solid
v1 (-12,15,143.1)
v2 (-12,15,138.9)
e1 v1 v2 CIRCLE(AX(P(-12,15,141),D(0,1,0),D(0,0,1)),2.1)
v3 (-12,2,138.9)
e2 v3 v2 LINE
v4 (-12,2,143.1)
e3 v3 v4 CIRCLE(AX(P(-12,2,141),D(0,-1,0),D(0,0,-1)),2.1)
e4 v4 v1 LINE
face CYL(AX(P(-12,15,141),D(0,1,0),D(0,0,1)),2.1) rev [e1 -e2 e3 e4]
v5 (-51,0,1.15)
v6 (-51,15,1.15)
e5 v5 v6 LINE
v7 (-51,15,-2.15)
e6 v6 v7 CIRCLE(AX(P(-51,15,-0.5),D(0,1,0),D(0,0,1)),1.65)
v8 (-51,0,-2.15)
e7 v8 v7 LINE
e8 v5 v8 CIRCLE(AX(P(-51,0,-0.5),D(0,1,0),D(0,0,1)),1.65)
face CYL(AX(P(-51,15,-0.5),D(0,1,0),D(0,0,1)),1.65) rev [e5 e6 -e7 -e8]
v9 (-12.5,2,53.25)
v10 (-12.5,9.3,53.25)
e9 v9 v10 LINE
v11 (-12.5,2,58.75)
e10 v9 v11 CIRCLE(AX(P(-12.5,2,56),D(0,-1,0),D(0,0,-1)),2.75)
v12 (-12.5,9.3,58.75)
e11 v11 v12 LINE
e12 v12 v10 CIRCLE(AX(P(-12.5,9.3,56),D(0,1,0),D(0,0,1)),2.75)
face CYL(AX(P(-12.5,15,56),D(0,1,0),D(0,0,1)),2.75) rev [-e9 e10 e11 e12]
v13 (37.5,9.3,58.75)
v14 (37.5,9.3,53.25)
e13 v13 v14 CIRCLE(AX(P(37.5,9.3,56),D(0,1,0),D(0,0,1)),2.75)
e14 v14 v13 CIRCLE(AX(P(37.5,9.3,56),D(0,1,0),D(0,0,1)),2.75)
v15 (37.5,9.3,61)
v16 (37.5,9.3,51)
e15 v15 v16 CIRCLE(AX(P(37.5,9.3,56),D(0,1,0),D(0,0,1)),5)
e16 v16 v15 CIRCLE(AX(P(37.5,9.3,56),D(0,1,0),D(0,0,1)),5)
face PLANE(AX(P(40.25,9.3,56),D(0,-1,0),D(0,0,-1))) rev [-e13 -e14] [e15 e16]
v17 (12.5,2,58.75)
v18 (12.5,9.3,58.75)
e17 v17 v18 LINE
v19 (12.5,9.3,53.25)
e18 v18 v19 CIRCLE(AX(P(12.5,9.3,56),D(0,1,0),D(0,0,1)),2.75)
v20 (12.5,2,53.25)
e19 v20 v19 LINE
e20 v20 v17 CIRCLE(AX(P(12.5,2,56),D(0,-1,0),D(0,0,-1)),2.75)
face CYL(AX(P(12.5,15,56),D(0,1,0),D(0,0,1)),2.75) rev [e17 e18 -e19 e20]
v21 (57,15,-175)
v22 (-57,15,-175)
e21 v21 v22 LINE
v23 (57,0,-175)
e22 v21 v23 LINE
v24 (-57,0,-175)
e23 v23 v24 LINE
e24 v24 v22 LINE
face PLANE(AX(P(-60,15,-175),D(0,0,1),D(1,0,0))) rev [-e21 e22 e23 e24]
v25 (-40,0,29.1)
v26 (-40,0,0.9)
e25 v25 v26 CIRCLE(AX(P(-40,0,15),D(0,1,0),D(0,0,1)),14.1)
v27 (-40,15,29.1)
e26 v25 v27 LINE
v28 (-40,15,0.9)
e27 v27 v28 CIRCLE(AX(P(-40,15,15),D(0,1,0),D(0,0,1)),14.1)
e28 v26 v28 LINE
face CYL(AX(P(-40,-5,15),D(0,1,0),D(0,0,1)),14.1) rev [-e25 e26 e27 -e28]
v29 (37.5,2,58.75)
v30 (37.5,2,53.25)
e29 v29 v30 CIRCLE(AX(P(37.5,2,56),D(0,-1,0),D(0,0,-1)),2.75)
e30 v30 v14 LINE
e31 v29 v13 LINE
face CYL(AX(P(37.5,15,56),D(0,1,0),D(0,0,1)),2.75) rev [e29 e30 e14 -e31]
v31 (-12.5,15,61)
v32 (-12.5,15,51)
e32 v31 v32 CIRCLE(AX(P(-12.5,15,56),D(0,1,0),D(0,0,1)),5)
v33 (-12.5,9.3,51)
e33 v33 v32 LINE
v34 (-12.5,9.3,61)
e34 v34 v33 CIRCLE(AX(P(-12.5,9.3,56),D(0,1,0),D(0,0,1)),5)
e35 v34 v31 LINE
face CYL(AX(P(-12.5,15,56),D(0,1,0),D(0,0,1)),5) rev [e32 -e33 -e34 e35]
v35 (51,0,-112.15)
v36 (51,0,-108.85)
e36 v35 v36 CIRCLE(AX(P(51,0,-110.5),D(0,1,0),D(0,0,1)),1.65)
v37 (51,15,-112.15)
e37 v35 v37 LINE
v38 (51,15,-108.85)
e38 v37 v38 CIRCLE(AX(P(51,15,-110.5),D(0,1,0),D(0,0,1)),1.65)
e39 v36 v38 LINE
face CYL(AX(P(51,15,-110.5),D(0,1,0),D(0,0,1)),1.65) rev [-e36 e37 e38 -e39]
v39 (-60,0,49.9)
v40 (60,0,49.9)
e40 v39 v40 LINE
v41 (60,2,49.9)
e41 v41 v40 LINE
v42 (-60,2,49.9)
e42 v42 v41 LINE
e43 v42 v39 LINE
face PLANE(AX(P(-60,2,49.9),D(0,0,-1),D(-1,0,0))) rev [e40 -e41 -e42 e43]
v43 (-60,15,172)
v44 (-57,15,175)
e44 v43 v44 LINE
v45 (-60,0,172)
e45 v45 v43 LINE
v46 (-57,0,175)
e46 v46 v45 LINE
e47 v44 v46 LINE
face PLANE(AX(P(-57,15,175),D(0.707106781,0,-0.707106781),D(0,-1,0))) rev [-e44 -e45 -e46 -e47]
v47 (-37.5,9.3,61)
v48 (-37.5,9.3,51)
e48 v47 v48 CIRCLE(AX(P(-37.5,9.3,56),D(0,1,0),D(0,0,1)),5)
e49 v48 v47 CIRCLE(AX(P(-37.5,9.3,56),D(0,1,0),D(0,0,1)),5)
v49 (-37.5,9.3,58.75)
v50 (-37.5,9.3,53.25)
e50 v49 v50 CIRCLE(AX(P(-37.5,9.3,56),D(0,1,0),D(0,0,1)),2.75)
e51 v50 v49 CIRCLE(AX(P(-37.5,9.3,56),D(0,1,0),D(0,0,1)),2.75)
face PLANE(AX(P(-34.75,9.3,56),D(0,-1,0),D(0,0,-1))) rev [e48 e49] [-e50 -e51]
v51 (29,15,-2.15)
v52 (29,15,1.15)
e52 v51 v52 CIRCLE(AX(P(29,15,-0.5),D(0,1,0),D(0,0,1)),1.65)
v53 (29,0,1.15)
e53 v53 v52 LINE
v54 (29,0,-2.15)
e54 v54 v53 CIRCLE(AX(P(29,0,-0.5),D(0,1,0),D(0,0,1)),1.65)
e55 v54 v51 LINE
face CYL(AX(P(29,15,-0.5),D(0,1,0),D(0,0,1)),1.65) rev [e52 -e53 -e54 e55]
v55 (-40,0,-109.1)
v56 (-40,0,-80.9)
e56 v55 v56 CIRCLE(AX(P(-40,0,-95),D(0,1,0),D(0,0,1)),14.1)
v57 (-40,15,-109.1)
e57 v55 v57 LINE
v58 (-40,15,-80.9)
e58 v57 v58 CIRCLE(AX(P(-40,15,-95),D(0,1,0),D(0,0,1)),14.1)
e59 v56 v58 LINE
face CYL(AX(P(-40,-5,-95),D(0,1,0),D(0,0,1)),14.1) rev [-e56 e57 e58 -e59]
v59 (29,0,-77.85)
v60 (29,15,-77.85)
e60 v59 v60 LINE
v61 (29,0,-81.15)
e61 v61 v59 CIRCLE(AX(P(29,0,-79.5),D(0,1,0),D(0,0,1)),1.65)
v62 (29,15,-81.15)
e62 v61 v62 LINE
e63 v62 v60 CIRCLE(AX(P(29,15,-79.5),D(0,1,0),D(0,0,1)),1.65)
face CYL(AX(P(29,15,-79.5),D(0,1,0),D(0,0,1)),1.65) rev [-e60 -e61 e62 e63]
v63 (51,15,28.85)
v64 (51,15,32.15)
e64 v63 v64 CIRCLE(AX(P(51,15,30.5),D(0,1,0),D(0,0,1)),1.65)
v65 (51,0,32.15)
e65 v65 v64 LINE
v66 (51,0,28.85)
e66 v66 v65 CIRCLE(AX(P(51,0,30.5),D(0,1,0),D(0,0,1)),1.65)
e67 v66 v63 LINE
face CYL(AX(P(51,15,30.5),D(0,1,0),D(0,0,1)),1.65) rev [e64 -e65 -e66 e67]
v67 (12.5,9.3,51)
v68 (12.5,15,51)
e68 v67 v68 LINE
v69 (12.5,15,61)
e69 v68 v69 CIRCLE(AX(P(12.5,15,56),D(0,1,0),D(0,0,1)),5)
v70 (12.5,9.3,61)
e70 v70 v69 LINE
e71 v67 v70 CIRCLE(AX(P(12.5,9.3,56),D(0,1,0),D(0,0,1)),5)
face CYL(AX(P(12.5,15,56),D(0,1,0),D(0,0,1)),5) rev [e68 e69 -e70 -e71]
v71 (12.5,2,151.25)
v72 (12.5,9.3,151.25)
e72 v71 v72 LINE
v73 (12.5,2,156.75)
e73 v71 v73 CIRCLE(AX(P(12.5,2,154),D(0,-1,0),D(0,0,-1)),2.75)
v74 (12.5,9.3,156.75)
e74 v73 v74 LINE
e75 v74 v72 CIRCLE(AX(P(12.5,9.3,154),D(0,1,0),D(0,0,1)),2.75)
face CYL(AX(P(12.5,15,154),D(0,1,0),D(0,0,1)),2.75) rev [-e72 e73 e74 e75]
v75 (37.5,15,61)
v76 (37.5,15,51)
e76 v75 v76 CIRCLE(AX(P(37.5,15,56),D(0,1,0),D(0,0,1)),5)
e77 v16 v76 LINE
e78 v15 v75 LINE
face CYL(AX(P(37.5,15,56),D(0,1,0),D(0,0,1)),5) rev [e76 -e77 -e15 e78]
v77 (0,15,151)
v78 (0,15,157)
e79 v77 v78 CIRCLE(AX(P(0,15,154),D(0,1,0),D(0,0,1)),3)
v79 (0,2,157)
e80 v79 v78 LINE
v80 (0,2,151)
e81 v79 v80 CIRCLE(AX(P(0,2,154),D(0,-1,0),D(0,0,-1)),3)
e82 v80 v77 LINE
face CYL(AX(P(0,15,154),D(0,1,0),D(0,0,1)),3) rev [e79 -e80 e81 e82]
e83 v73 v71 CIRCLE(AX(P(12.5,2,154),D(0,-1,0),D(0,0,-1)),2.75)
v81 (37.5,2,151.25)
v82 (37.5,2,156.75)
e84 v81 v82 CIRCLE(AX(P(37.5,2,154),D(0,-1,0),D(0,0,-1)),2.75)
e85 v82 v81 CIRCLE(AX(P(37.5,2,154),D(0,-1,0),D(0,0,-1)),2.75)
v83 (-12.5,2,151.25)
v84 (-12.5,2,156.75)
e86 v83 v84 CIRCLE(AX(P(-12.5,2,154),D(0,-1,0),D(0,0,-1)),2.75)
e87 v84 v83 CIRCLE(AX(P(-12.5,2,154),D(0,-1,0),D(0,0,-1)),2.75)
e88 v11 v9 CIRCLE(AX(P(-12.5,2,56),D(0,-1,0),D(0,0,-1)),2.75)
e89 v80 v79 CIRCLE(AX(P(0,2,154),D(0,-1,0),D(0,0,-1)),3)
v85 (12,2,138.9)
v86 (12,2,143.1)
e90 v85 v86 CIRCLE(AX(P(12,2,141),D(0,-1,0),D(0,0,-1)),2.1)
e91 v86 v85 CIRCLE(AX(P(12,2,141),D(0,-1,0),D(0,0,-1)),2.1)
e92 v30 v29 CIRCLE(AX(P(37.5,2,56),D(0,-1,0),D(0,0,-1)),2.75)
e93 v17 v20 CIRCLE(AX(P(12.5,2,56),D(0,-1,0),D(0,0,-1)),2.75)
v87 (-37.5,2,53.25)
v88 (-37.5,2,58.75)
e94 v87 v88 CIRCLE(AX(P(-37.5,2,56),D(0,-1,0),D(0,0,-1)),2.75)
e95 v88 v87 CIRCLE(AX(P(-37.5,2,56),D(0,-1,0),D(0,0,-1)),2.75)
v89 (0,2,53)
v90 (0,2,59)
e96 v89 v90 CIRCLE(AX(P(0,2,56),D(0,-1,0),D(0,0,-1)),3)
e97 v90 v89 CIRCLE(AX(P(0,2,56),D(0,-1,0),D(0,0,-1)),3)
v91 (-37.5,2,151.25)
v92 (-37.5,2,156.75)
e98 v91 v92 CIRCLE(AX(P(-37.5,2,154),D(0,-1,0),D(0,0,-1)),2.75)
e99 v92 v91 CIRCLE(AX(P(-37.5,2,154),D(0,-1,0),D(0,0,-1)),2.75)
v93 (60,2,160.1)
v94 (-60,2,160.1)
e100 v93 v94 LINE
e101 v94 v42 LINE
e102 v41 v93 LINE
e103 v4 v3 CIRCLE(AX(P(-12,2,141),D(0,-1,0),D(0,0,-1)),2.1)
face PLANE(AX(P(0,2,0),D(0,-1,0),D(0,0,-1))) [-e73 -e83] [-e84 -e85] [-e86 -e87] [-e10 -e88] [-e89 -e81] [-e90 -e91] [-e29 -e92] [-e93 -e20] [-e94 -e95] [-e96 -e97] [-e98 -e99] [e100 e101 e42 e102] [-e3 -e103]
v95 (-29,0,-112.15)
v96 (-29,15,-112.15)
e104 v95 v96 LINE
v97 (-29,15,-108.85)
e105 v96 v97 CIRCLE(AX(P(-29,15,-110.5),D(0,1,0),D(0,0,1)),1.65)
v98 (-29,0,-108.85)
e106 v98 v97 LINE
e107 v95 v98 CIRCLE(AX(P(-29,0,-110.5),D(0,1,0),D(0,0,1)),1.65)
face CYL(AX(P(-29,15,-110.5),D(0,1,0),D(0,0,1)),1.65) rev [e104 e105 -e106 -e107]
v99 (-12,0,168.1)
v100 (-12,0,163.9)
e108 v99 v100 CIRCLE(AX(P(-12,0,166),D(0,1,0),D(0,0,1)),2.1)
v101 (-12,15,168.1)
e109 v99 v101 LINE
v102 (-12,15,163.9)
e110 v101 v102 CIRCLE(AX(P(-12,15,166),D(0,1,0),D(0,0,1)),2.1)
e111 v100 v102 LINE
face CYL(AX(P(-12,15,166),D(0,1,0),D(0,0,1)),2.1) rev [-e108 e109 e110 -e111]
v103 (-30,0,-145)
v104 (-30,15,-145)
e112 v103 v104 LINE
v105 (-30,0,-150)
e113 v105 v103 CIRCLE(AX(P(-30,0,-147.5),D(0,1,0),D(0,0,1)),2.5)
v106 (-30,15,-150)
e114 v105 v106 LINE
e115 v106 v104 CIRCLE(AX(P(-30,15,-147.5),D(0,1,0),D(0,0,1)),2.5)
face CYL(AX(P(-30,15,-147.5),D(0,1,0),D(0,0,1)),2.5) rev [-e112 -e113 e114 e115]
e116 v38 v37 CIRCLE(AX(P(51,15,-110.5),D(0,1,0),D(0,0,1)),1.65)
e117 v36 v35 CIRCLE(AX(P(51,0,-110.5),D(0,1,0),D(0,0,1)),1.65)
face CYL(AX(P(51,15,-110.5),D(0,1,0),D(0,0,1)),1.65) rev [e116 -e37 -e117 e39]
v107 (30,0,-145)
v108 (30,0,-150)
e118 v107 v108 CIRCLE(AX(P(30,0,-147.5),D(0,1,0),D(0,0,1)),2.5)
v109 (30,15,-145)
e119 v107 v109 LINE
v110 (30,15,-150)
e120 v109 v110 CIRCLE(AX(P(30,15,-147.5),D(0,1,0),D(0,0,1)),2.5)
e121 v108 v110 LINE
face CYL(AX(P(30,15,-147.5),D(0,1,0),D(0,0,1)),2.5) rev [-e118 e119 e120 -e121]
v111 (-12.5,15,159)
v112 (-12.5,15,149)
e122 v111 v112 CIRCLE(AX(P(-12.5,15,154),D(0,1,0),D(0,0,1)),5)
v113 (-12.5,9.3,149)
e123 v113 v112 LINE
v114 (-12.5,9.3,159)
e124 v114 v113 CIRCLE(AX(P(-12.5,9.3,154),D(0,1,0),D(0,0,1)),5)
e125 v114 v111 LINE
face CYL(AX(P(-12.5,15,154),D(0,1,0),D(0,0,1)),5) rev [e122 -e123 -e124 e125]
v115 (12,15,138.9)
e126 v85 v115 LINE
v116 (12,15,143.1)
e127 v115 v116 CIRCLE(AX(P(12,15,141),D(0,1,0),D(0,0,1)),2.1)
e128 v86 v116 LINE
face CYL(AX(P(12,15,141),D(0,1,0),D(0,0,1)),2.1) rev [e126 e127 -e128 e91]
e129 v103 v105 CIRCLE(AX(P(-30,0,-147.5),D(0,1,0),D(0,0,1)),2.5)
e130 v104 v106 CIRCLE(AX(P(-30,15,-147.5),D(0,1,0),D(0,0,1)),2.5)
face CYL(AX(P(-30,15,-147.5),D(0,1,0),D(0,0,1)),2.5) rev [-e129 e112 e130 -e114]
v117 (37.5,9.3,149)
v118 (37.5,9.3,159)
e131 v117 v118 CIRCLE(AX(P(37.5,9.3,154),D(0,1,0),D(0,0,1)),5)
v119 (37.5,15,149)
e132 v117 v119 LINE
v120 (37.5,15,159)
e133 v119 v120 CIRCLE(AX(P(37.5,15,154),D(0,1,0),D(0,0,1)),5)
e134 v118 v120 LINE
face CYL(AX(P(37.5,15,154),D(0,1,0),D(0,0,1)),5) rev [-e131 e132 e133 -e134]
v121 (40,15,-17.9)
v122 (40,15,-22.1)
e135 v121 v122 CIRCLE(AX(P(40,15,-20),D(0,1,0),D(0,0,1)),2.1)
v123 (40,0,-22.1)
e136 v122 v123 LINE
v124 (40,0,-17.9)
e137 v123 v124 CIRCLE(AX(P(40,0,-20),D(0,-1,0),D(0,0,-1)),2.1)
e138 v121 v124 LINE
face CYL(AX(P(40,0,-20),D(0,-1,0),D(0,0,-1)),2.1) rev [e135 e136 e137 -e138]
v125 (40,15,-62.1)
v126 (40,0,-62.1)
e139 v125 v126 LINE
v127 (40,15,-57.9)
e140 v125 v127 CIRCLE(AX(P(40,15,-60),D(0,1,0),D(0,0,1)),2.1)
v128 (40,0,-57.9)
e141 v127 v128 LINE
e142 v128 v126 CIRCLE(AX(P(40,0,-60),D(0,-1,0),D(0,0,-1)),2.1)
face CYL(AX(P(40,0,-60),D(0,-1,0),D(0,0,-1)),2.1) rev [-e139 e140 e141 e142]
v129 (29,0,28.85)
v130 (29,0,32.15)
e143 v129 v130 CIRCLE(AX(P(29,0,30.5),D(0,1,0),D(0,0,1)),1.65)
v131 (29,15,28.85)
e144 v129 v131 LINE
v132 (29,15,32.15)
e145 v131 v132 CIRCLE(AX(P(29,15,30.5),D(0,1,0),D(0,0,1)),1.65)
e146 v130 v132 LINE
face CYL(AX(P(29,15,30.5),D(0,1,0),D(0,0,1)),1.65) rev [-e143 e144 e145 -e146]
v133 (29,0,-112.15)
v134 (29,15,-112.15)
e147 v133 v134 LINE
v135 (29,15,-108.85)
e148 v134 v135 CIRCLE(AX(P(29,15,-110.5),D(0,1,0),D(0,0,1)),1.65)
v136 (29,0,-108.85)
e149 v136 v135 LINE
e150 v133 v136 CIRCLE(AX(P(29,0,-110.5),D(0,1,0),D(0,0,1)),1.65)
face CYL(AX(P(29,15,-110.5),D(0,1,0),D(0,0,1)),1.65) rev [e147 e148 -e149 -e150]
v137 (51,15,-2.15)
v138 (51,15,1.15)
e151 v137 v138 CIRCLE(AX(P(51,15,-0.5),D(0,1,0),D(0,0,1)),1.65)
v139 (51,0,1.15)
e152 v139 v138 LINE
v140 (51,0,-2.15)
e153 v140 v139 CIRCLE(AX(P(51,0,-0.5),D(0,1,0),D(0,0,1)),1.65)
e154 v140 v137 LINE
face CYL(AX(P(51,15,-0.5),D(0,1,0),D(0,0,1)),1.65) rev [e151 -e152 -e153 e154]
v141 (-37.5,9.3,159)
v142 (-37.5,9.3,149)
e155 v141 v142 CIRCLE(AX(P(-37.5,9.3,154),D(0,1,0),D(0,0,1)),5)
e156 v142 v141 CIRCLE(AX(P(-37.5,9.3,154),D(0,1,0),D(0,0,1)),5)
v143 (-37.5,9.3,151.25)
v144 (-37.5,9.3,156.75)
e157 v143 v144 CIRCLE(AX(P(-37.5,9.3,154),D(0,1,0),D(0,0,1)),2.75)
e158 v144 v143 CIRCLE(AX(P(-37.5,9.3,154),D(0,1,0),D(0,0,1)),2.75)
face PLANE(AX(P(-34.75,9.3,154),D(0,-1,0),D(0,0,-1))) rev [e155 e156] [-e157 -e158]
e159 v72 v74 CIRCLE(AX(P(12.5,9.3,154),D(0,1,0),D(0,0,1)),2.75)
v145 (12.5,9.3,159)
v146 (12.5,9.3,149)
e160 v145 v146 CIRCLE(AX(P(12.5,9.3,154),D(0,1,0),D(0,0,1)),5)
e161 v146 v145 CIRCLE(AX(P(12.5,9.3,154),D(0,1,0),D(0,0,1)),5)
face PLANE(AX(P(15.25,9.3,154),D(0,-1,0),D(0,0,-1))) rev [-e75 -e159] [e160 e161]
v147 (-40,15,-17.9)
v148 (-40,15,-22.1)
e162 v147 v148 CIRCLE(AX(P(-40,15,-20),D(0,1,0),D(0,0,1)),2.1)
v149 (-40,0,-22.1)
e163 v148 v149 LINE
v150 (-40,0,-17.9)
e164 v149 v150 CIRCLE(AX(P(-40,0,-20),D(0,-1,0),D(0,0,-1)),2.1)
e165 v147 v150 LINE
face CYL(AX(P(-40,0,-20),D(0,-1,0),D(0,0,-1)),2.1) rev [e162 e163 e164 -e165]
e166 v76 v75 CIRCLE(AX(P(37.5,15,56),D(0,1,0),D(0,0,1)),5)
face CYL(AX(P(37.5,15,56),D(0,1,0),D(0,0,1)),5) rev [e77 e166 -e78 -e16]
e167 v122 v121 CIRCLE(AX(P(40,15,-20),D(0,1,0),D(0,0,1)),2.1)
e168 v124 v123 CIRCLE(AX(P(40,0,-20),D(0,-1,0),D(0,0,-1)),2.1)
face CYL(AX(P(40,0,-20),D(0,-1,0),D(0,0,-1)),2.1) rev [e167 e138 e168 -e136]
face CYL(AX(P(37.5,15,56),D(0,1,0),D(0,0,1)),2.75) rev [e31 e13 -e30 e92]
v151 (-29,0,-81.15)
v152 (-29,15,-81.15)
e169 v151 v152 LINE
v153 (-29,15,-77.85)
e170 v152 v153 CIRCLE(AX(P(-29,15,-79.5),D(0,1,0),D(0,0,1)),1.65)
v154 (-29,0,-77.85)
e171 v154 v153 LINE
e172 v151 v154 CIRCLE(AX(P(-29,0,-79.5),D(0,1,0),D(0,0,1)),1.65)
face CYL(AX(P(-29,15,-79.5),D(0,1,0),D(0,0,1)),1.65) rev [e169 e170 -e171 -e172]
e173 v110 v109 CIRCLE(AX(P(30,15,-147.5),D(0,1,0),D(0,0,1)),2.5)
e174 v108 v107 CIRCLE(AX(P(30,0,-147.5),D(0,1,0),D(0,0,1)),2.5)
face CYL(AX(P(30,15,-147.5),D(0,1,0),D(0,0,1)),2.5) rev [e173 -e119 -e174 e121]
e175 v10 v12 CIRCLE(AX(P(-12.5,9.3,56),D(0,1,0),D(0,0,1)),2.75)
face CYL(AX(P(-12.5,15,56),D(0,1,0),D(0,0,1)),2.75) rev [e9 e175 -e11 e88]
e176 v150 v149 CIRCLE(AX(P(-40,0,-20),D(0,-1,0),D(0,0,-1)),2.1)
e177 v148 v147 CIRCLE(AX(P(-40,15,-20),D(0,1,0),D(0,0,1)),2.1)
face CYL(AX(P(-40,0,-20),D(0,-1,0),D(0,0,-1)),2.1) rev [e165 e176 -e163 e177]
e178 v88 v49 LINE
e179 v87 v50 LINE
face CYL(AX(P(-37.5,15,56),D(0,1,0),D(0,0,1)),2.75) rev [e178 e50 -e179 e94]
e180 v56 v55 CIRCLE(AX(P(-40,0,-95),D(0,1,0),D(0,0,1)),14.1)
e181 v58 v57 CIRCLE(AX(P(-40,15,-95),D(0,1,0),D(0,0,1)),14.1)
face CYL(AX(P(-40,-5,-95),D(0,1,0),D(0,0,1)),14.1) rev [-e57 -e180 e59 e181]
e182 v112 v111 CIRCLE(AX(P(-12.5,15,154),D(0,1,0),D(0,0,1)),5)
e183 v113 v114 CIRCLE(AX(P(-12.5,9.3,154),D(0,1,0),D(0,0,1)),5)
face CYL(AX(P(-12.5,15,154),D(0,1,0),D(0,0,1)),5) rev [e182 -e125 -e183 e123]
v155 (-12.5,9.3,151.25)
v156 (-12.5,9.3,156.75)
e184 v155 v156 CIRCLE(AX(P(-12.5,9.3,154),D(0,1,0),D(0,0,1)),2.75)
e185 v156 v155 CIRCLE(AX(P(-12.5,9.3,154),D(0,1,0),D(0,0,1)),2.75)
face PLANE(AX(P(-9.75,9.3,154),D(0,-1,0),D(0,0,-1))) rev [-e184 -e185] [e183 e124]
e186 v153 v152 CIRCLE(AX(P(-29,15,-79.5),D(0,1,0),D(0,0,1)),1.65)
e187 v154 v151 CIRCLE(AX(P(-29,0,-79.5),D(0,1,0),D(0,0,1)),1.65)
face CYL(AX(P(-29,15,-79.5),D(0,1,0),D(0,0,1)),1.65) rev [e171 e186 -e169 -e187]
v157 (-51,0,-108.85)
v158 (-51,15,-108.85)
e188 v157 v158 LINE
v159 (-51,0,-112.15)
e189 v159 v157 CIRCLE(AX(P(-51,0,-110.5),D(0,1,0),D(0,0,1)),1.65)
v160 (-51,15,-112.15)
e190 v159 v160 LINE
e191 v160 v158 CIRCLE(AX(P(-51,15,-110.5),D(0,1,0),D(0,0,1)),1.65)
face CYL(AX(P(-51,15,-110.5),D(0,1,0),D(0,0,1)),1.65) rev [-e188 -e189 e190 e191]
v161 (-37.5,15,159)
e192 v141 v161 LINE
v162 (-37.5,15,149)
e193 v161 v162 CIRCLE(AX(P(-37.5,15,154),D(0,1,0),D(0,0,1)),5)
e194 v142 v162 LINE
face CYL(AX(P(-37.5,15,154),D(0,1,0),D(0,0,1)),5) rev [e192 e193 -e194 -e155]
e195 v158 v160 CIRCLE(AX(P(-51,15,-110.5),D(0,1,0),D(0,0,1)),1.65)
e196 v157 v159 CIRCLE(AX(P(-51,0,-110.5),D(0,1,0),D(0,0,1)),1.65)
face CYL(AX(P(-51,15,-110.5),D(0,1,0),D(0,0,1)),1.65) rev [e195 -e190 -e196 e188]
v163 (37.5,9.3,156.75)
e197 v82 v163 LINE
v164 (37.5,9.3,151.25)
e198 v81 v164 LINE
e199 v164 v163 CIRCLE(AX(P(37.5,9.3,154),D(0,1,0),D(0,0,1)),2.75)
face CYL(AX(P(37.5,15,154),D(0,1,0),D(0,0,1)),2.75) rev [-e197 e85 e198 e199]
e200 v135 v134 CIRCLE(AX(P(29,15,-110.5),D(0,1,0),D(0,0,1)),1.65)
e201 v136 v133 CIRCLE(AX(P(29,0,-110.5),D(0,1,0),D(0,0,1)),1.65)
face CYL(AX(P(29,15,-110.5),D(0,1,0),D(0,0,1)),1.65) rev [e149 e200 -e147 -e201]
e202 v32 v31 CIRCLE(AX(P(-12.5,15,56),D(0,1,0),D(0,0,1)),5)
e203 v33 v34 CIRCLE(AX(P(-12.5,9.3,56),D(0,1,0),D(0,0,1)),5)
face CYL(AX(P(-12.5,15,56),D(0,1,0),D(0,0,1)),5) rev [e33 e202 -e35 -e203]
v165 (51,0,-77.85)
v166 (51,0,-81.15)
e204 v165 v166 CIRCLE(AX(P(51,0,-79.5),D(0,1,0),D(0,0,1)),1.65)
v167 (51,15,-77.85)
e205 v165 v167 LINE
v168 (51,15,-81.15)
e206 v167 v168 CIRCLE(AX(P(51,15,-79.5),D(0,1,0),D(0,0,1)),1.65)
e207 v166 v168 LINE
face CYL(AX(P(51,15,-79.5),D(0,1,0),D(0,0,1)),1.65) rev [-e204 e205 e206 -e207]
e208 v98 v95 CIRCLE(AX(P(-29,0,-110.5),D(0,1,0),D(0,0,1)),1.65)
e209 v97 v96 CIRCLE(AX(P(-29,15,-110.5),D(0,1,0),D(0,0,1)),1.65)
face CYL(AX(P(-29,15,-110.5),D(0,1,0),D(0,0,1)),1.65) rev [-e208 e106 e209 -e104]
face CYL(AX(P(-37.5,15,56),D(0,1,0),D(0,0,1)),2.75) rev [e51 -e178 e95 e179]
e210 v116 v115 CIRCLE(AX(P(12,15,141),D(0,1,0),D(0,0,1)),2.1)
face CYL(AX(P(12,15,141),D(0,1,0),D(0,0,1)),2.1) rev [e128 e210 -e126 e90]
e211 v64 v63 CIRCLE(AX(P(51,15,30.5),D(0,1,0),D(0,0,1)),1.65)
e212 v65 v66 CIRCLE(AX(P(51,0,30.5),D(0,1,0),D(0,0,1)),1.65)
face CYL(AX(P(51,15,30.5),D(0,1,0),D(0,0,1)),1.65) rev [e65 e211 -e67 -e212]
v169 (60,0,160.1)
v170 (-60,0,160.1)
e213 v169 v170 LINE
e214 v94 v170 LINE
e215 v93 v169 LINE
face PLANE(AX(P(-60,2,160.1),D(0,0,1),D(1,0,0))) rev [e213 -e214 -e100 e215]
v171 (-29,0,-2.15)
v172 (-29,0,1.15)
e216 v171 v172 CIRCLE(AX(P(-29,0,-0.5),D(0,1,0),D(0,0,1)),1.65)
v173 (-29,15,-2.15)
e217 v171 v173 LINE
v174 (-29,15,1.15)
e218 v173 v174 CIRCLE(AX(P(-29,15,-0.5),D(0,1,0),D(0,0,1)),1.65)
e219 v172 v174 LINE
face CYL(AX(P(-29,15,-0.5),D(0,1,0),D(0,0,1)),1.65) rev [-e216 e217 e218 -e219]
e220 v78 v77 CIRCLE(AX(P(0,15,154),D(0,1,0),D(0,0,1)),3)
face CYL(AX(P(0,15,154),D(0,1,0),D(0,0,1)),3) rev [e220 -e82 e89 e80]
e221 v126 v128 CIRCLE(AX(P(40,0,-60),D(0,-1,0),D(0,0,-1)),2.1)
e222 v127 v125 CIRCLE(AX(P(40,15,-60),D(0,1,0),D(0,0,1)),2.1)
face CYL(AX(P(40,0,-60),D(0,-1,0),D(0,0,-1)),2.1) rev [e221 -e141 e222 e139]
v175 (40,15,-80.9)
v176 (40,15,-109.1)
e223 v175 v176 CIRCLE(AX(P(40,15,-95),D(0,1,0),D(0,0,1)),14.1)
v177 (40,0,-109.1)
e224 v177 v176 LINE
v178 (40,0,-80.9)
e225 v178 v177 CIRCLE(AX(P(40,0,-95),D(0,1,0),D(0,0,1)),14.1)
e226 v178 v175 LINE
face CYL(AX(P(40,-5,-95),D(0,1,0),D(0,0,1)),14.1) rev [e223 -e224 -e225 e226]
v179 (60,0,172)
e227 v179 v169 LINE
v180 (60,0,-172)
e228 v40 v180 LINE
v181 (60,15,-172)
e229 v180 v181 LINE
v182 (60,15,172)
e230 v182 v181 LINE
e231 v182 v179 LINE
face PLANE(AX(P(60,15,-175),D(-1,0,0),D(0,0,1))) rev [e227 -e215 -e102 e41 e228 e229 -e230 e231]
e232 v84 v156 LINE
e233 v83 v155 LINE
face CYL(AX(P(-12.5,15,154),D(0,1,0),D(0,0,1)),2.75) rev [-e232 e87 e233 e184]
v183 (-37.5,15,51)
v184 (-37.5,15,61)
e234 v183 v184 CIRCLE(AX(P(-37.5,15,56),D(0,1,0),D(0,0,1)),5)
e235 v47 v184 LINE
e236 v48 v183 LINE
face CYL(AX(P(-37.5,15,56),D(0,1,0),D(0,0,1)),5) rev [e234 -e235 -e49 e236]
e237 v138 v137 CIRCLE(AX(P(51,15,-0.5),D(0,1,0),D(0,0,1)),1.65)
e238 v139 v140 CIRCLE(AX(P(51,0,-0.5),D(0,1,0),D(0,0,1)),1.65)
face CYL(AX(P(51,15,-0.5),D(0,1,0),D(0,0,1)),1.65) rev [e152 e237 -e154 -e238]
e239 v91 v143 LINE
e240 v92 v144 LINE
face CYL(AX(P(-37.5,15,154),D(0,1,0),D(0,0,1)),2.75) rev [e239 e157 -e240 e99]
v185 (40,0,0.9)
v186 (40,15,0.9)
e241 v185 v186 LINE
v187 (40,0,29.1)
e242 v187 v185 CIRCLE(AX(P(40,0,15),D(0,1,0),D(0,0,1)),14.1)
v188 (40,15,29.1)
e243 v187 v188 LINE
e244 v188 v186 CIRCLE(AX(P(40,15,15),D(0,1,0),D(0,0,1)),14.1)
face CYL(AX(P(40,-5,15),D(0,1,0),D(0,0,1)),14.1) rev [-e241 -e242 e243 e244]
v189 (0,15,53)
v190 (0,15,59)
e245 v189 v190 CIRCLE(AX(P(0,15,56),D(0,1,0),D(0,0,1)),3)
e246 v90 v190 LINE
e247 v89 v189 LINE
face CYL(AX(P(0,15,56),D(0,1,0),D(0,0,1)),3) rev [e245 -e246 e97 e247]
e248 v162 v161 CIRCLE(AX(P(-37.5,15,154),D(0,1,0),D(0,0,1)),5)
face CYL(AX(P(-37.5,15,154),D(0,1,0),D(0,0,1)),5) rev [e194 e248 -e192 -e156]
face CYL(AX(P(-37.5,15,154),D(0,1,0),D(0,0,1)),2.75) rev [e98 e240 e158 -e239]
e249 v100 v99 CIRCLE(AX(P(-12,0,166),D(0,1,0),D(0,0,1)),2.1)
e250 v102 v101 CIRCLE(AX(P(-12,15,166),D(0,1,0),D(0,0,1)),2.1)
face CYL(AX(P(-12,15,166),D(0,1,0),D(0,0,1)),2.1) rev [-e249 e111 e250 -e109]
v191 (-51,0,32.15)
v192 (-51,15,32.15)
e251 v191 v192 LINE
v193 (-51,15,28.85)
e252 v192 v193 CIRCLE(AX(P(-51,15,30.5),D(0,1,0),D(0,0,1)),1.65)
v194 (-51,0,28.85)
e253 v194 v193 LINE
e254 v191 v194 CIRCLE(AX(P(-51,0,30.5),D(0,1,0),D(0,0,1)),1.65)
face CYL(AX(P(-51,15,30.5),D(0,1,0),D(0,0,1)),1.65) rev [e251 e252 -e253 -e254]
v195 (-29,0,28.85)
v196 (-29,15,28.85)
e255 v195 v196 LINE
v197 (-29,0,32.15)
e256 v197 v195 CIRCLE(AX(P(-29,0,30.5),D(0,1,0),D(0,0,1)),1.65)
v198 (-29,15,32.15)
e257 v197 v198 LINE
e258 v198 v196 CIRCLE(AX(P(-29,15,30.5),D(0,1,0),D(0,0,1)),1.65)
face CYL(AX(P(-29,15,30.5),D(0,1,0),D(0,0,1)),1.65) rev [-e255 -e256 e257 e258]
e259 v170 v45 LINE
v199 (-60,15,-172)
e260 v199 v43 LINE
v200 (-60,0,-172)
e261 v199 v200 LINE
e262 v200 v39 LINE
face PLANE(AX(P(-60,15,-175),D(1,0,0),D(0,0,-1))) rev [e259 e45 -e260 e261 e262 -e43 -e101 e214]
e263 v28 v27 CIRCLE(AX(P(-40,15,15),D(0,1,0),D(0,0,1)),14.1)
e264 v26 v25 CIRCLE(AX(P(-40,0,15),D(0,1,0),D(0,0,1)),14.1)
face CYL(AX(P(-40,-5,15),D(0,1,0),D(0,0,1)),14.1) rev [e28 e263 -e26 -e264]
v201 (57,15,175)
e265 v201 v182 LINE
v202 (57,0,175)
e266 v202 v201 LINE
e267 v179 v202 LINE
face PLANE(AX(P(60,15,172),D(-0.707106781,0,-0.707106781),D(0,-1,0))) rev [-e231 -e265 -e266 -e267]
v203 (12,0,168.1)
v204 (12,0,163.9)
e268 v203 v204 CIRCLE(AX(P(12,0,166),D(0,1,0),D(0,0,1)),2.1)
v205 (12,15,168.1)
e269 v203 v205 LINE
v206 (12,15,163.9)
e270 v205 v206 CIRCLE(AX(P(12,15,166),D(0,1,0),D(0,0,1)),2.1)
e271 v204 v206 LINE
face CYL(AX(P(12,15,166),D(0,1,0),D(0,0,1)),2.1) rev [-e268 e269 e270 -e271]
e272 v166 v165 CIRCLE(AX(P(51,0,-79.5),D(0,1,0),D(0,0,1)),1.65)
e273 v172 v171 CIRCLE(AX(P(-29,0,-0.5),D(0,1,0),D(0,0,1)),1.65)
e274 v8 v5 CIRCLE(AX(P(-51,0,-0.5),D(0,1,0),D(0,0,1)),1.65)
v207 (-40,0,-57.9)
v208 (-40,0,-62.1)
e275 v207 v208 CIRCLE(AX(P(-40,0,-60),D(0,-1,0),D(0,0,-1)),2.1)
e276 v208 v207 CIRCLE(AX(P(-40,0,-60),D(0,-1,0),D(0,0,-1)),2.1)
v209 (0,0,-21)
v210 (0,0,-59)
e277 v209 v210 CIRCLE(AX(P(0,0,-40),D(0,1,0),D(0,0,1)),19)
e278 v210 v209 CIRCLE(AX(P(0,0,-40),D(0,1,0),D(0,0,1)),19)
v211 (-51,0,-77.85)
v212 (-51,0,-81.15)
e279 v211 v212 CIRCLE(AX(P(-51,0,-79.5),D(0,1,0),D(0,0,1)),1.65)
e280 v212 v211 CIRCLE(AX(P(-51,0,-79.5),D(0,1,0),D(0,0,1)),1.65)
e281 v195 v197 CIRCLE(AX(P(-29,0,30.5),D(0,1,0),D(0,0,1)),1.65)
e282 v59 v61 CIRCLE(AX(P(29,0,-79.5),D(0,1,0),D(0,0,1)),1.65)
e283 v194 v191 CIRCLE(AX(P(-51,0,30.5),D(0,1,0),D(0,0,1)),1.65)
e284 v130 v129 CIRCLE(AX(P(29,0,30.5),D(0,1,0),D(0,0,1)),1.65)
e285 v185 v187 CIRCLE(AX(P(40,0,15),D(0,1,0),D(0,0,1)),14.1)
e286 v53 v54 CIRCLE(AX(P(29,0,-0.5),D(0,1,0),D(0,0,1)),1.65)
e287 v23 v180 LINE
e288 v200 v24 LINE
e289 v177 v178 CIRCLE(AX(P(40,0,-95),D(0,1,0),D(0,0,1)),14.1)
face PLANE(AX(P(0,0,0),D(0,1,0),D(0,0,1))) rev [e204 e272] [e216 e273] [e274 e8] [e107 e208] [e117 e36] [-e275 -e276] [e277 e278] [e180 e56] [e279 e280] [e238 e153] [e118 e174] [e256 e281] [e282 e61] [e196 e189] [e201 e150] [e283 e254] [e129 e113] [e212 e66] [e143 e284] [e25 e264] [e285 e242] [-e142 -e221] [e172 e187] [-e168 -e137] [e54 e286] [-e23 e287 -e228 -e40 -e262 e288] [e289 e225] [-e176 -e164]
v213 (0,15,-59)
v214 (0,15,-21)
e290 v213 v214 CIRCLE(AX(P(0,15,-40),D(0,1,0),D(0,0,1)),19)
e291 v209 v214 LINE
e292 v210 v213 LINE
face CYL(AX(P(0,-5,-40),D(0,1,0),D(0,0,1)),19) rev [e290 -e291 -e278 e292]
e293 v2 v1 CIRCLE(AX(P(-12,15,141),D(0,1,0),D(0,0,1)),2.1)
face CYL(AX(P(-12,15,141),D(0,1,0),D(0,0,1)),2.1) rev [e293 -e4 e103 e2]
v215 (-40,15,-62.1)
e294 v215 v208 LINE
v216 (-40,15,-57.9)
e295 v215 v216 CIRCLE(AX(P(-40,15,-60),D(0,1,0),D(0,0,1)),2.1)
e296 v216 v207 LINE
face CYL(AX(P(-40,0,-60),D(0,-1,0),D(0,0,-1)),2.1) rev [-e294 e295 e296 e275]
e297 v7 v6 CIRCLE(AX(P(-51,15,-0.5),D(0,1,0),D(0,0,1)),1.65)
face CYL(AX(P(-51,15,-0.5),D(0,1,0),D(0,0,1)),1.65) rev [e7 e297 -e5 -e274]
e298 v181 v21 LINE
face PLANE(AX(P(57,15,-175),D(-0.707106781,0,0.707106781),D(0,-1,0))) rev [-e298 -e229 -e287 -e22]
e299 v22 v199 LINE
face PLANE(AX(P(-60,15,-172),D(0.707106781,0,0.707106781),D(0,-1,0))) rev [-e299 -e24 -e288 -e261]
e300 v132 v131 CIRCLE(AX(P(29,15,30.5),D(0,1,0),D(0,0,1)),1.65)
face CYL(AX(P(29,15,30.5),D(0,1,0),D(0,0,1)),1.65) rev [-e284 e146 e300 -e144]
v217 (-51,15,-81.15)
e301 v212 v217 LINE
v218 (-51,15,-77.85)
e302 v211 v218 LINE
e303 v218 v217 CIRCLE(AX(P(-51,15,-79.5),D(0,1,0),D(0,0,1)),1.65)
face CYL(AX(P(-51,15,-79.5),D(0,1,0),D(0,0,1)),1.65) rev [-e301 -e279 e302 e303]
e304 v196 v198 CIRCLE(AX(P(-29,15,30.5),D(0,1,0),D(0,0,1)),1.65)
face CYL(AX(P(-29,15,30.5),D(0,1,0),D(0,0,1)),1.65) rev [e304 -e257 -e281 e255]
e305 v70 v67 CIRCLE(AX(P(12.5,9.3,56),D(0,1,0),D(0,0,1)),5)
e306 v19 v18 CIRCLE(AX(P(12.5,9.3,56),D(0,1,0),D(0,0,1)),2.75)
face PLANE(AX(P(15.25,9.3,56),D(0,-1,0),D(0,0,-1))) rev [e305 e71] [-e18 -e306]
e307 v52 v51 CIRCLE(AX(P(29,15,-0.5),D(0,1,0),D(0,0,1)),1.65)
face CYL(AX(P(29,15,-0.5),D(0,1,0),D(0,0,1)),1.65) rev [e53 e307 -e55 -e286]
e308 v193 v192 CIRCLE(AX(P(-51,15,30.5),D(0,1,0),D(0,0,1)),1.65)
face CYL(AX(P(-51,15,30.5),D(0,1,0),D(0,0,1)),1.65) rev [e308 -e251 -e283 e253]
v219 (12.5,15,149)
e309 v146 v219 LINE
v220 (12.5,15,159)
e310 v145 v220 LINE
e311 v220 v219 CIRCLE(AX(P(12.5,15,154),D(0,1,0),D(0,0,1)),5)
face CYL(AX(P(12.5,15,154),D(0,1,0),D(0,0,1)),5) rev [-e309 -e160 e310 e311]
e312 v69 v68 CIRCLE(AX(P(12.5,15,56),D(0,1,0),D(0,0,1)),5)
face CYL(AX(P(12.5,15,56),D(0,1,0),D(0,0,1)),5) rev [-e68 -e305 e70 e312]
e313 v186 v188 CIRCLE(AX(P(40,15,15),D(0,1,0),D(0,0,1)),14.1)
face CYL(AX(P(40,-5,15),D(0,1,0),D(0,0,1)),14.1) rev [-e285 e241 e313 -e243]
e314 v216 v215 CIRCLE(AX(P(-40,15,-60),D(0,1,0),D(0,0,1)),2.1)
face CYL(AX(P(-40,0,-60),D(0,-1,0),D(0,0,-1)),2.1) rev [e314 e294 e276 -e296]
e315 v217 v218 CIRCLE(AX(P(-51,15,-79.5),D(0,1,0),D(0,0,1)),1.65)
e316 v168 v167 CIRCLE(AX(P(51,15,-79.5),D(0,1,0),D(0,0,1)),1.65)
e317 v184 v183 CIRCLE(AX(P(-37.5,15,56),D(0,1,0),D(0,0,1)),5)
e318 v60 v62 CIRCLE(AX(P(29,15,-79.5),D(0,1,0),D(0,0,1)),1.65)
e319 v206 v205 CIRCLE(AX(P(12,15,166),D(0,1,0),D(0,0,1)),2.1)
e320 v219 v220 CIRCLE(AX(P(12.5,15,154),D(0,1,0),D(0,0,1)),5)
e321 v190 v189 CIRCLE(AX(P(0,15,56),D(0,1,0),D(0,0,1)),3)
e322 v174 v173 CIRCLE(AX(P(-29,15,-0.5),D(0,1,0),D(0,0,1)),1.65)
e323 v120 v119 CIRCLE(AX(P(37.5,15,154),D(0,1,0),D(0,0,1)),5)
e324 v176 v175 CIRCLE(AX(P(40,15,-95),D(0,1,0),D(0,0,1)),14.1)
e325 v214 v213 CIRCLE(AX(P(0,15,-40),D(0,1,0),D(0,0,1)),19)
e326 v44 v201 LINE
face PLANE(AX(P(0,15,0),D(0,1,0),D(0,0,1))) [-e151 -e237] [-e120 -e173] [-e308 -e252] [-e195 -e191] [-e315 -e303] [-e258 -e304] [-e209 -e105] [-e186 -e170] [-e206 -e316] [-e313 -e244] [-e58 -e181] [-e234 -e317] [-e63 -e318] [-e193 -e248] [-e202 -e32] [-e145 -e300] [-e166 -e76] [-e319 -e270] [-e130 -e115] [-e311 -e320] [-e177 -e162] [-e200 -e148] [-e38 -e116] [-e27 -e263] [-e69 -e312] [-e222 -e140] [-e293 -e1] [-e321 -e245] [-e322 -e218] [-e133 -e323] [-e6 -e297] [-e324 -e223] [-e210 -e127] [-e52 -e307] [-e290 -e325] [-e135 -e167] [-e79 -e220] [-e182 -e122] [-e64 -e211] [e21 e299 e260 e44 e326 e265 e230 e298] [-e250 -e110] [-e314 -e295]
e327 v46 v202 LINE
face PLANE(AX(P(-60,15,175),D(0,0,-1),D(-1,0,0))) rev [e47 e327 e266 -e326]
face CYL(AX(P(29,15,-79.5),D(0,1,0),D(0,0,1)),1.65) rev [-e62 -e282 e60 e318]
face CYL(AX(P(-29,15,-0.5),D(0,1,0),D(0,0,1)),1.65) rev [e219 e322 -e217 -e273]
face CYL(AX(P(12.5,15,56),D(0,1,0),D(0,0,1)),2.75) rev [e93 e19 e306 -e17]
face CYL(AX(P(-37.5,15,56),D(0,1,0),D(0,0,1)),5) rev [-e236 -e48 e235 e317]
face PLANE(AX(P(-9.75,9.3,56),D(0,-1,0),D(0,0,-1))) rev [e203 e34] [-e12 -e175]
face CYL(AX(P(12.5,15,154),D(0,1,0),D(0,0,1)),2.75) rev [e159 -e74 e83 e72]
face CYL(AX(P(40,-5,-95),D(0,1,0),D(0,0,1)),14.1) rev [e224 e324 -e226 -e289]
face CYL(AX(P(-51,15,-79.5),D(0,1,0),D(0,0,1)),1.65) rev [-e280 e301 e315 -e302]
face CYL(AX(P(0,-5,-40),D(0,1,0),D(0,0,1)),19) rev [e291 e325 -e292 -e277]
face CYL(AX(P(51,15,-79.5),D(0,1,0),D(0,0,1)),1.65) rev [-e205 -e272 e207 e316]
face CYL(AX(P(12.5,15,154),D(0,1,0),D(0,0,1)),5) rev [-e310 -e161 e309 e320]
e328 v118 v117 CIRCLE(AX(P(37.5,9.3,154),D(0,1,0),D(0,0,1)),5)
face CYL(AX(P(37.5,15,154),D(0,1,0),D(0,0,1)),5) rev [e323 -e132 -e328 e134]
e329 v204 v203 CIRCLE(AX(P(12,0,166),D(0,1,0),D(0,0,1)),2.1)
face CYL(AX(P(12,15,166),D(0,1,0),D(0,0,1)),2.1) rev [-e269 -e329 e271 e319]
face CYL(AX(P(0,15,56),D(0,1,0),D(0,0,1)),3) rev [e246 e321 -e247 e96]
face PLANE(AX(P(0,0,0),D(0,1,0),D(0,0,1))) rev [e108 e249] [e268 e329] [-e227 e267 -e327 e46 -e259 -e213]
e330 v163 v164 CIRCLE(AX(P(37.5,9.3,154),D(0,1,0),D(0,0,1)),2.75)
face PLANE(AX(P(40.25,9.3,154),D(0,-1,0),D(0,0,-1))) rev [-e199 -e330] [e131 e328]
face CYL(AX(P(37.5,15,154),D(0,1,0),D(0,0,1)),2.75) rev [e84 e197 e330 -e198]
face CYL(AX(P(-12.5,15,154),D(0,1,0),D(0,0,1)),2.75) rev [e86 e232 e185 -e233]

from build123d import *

# Parameters (mm, degrees)
SKETCH_1_W                = 120
SKETCH_1_H                = 350
EXTRUDE_1_DEPTH           = 15
SKETCH_3_W                = 120
SKETCH_3_H                = 110.2
CUT_EXTRUDE_1_DEPTH       = 2
HOLE_WIZARD_0_D           = 5.5
HOLE_WIZARD_0_DEPTH       = 25
HOLE_WIZARD_0_CBORE_D     = 10
HOLE_WIZARD_0_CBORE_DEPTH = 5.7
HOLE_WIZARD_0_TIP         = 1.652366702
MM_1_D                    = 6
MM_1_DEPTH                = 25
MM_1_TIP                  = 1.802581857
CHAMFER_1_SIZE            = 3
SKETCH_8_R                = 19
CUT_EXTRUDE_2_DEPTH       = 20
SKETCH_9_R                = 14.1
CUT_EXTRUDE_3_DEPTH       = 20
MM_2_D                    = 5
MM_2_DEPTH                = 20
MM_2_TIP                  = 1.502151548
HOLE_WIZARD_M5_1_D        = 4.2
HOLE_WIZARD_M5_1_DEPTH    = 20
HOLE_WIZARD_M5_1_TIP      = 1.2618073
HOLE_WIZARD_M4_1_D        = 3.3
HOLE_WIZARD_M4_1_DEPTH    = 32
HOLE_WIZARD_M4_1_TIP      = 0.991420021
HOLE_WIZARD_M5_2_D        = 4.2
HOLE_WIZARD_M5_2_DEPTH    = 20
HOLE_WIZARD_M5_2_TIP      = 1.2618073


with BuildPart() as part:
    # 草图1 → 凸台-拉伸1 (new body)
    with BuildSketch(Plane(origin=(0, 0, 0), x_dir=(1, 0, 0), z_dir=(0, 1, 0))):
        Rectangle(SKETCH_1_W, SKETCH_1_H)
    extrude(amount=EXTRUDE_1_DEPTH)

    # 草图3 → 切除-拉伸1 (cut)
    with BuildSketch(Plane.XZ):
        with Locations((0, 105)):
            Rectangle(SKETCH_3_W, SKETCH_3_H)
    extrude(amount=-CUT_EXTRUDE_1_DEPTH, mode=Mode.SUBTRACT)

    # 打孔尺寸(%根据)内六角圆柱头螺钉的类型0
    with Locations(Plane(origin=(0, 15, 0), x_dir=(1, 0, 0), z_dir=(0, 1, 0))):
        with Locations((-37.5, -154), (-12.5, -154), (12.5, -154), (37.5, -154), (-37.5, -56), (-12.5, -56), (12.5, -56), (37.5, -56)):
            CounterBoreHole(HOLE_WIZARD_0_D / 2, HOLE_WIZARD_0_CBORE_D / 2, HOLE_WIZARD_0_CBORE_DEPTH, depth=HOLE_WIZARD_0_DEPTH)
            with Locations((0, 0, -(HOLE_WIZARD_0_DEPTH + HOLE_WIZARD_0_TIP / 2))):  # 118° drill point
                Cone(0, HOLE_WIZARD_0_D / 2, HOLE_WIZARD_0_TIP, mode=Mode.SUBTRACT)

    # 大小mm 暗销孔1
    with Locations(Plane(origin=(0, 15, 0), x_dir=(1, 0, 0), z_dir=(0, 1, 0))):
        with Locations((0, -154), (0, -56)):
            Hole(MM_1_D / 2, depth=MM_1_DEPTH)
            with Locations((0, 0, -(MM_1_DEPTH + MM_1_TIP / 2))):  # 118° drill point
                Cone(0, MM_1_D / 2, MM_1_TIP, mode=Mode.SUBTRACT)

    # 倒角1
    chamfer_1_edges = [part.edges().sort_by_distance(p)[0] for p in [
        (60, 7.5, 175),
        (-60, 7.5, 175),
        (-60, 7.5, -175),
        (60, 7.5, -175),
    ]]
    chamfer(chamfer_1_edges, length=CHAMFER_1_SIZE)

    # 草图8 → 切除-拉伸2 (cut)
    with BuildSketch(Plane(origin=(0, 15, 0), x_dir=(1, 0, 0), z_dir=(0, 1, 0))):
        with Locations(Location((0, 40, 0), (0, 0, 270))):
            Circle(SKETCH_8_R)
    extrude(amount=-CUT_EXTRUDE_2_DEPTH, mode=Mode.SUBTRACT)

    # 草图9 → 切除-拉伸3 (cut)
    with BuildSketch(Plane(origin=(0, 15, 0), x_dir=(1, 0, 0), z_dir=(0, 1, 0))):
        with Locations(Location((40, -15, 0), (0, 0, 270))):
            Circle(SKETCH_9_R)
        with Locations(Location((40, 95, 0), (0, 0, 270))):
            Circle(SKETCH_9_R)
        with Locations(Location((-40, -15, 0), (0, 0, 270))):
            Circle(SKETCH_9_R)
        with Locations(Location((-40, 95, 0), (0, 0, 270))):
            Circle(SKETCH_9_R)
    extrude(amount=-CUT_EXTRUDE_3_DEPTH, mode=Mode.SUBTRACT)

    # 大小mm 暗销孔2
    with Locations(Plane(origin=(0, 15, 0), x_dir=(1, 0, 0), z_dir=(0, 1, 0))):
        with Locations((29.999999981, 147.499999979), (-30.000000019, 147.499999979)):
            Hole(MM_2_D / 2, depth=MM_2_DEPTH)
            with Locations((0, 0, -(MM_2_DEPTH + MM_2_TIP / 2))):  # 118° drill point
                Cone(0, MM_2_D / 2, MM_2_TIP, mode=Mode.SUBTRACT)

    # M5 螺纹孔1
    with Locations(Plane(origin=(0, 0, 0), x_dir=(-1, 0, 0), z_dir=(0, -1, 0))):
        with Locations((39.999999998, 19.999999998), (-40.000000002, 19.999999998), (39.999999998, 59.999999998), (-40.000000002, 59.999999998)):
            Hole(HOLE_WIZARD_M5_1_D / 2, depth=HOLE_WIZARD_M5_1_DEPTH)
            with Locations((0, 0, -(HOLE_WIZARD_M5_1_DEPTH + HOLE_WIZARD_M5_1_TIP / 2))):  # 118° drill point
                Cone(0, HOLE_WIZARD_M5_1_D / 2, HOLE_WIZARD_M5_1_TIP, mode=Mode.SUBTRACT)

    # M4 螺纹孔1
    with Locations(Plane(origin=(0, 15, 0), x_dir=(1, 0, 0), z_dir=(0, 1, 0))):
        with Locations((51, -30.5), (29, -30.5), (51, 0.5), (29, 0.5), (-51, -30.5), (-29, -30.5), (-29, 0.5), (-51, 0.5), (51, 79.5), (29, 79.5), (51, 110.5), (29, 110.5), (-29, 79.5), (-51, 79.5), (-29, 110.5), (-51, 110.5)):
            Hole(HOLE_WIZARD_M4_1_D / 2, depth=HOLE_WIZARD_M4_1_DEPTH)
            with Locations((0, 0, -(HOLE_WIZARD_M4_1_DEPTH + HOLE_WIZARD_M4_1_TIP / 2))):  # 118° drill point
                Cone(0, HOLE_WIZARD_M4_1_D / 2, HOLE_WIZARD_M4_1_TIP, mode=Mode.SUBTRACT)

    # M5 螺纹孔2
    with Locations(Plane(origin=(0, 15, 0), x_dir=(1, 0, 0), z_dir=(0, 1, 0))):
        with Locations((-11.999999999, -141.000000001), (12.000000001, -141.000000001), (-11.999999999, -166.000000001), (12.000000001, -166.000000001)):
            Hole(HOLE_WIZARD_M5_2_D / 2, depth=HOLE_WIZARD_M5_2_DEPTH)
            with Locations((0, 0, -(HOLE_WIZARD_M5_2_DEPTH + HOLE_WIZARD_M5_2_TIP / 2))):  # 118° drill point
                Cone(0, HOLE_WIZARD_M5_2_D / 2, HOLE_WIZARD_M5_2_TIP, mode=Mode.SUBTRACT)


solid = part.part
